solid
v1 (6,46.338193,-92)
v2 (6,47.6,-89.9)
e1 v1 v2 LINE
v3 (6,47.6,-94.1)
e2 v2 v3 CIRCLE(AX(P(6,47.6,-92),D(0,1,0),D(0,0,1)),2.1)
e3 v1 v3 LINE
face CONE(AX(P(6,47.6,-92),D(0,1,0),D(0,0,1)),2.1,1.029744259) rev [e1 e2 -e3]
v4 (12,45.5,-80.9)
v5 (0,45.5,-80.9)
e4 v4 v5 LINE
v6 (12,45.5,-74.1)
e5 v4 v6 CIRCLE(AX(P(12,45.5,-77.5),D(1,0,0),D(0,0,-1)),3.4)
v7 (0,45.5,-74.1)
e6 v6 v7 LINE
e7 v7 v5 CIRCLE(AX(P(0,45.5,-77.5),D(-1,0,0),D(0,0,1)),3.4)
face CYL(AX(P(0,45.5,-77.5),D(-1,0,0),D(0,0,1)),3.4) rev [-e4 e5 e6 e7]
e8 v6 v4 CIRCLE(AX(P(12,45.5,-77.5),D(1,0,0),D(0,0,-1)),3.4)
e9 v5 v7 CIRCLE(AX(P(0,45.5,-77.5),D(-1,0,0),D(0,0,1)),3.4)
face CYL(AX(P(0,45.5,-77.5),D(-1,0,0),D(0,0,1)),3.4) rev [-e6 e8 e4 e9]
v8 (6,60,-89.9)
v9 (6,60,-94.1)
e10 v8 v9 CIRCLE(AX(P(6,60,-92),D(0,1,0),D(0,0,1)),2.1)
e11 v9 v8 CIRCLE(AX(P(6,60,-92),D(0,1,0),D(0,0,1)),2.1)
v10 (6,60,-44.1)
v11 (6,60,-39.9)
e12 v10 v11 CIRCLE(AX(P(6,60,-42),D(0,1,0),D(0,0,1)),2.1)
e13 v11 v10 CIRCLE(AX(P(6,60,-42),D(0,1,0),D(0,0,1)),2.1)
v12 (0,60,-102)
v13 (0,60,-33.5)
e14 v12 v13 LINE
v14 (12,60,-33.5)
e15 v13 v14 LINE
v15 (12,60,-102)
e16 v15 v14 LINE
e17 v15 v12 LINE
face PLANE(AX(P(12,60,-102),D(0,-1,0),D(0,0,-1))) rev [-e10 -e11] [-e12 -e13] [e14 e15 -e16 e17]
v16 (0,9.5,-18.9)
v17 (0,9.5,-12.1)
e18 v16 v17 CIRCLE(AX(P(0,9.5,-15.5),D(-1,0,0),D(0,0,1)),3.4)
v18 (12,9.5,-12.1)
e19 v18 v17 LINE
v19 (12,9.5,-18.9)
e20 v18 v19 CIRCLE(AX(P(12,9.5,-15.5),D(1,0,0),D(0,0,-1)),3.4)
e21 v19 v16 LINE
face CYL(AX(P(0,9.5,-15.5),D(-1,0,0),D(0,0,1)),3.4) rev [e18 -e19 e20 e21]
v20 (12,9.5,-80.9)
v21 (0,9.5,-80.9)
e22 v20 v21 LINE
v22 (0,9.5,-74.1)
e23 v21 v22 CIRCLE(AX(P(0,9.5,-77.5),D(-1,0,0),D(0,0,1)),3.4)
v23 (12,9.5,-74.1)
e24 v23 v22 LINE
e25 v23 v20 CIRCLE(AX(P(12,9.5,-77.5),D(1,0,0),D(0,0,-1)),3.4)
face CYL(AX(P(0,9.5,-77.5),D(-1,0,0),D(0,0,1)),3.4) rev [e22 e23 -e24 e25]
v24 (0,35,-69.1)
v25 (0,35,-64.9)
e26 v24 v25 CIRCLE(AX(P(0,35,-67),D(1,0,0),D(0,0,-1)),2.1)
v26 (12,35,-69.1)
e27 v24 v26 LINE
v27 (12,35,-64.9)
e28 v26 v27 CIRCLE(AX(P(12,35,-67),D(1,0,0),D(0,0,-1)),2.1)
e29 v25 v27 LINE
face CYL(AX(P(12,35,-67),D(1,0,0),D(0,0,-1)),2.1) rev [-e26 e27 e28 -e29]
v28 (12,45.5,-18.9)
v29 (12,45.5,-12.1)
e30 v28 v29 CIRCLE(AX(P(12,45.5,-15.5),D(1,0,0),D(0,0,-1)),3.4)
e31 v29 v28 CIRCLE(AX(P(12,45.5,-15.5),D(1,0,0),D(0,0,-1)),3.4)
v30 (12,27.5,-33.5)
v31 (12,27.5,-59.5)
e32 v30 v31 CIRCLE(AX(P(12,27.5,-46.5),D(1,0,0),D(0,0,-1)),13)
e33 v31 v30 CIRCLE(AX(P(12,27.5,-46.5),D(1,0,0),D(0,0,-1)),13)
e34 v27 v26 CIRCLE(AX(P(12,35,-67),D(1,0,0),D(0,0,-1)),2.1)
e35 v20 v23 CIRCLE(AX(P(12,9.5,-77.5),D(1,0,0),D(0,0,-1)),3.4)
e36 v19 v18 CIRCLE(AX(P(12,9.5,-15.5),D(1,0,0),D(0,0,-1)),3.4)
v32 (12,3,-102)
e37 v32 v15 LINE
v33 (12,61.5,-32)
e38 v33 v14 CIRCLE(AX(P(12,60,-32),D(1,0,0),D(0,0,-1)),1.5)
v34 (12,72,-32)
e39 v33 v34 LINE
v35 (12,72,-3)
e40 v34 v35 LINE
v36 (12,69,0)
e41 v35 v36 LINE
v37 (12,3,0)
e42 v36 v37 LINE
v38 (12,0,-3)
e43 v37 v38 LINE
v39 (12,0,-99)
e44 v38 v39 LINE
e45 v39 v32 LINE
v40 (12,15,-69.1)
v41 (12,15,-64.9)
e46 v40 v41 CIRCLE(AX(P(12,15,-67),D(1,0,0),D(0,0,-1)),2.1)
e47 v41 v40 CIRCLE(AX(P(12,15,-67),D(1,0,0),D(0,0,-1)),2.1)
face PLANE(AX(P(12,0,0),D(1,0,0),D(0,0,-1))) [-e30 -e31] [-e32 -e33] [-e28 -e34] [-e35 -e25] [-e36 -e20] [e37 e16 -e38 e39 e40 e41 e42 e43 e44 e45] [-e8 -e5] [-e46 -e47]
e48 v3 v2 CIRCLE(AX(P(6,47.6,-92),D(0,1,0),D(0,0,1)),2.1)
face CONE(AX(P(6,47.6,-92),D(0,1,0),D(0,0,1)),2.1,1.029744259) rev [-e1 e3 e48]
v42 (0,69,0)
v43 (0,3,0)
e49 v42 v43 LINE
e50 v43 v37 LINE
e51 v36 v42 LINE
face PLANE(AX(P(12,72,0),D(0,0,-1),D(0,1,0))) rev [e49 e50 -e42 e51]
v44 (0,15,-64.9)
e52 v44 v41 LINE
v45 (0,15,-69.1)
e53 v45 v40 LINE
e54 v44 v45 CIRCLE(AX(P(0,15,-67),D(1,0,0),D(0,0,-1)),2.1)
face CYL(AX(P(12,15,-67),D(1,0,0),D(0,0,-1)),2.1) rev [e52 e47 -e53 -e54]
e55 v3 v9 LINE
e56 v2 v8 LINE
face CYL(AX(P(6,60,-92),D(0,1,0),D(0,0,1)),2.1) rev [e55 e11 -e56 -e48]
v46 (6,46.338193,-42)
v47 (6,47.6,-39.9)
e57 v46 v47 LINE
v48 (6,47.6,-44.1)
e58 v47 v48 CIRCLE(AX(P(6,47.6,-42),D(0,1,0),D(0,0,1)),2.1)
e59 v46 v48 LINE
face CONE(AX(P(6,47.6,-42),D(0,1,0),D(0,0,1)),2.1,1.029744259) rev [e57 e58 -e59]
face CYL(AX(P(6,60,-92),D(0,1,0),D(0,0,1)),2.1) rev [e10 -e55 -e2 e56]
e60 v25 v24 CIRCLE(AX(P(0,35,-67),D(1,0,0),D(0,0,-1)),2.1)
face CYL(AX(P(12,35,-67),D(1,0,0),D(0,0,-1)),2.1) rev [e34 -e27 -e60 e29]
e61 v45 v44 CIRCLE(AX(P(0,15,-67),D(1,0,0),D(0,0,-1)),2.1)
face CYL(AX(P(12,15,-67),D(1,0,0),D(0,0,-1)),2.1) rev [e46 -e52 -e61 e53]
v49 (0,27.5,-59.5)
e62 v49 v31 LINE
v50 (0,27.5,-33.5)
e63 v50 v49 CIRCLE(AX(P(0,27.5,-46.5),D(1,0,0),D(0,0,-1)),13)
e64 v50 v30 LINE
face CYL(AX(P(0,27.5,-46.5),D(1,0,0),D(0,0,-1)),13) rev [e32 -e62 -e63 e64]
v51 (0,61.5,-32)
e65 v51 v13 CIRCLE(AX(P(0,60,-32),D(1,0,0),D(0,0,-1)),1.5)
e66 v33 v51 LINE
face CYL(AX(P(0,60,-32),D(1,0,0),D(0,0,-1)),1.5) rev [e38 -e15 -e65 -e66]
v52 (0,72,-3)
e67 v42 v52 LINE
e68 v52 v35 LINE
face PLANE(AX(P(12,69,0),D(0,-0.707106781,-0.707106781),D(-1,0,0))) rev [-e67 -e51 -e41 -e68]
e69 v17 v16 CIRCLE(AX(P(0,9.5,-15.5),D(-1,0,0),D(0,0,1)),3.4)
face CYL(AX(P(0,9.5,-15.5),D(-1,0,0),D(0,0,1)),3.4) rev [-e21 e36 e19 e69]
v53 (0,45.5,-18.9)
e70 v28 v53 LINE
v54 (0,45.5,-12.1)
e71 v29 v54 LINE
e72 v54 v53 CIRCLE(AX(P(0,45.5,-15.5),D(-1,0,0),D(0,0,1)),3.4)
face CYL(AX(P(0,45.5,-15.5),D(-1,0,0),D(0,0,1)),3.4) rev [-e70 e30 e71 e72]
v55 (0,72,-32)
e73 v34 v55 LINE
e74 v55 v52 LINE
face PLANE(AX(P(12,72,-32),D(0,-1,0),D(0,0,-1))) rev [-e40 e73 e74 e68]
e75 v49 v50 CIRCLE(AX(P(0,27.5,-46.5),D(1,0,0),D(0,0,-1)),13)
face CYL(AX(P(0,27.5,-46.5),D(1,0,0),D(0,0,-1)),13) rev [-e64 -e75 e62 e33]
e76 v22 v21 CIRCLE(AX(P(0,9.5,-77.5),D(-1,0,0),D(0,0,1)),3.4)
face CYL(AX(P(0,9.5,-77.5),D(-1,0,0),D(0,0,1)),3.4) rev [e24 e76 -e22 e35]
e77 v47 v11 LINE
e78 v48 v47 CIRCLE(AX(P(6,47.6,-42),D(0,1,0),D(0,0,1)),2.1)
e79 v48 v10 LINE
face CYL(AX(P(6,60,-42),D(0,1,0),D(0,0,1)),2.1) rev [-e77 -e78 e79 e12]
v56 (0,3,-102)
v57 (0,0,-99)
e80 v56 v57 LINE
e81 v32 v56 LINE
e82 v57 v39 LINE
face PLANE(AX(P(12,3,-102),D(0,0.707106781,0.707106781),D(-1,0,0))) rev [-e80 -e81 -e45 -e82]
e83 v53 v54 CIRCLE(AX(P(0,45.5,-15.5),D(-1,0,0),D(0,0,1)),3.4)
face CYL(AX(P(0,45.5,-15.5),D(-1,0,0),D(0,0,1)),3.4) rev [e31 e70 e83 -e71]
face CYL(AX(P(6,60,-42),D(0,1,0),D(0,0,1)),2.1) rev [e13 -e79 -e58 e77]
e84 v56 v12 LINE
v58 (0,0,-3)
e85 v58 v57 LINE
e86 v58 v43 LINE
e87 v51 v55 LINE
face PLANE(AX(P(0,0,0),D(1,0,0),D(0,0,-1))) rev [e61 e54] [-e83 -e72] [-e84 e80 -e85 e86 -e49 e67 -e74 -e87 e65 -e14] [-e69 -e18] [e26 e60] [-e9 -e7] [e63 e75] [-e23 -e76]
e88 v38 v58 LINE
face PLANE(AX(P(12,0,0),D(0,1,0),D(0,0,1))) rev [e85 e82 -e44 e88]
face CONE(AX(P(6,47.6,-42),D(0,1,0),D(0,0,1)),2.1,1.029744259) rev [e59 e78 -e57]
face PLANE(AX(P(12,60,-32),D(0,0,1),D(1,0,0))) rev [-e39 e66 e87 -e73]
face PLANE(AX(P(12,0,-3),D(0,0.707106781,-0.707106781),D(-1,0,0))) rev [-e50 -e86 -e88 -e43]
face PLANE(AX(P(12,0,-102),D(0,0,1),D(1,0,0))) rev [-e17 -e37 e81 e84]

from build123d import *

# Parameters (mm, degrees)
BOSS_EXTRUDE1_DEPTH   = 12
SKETCH2_R             = 13
CUT_EXTRUDE1_DEPTH    = 126.427269762
M8_TAPPED_HOLE1_D     = 6.8
M8_TAPPED_HOLE1_DEPTH = 19.75
M8_TAPPED_HOLE1_TIP   = 2.042926105
M5_TAPPED_HOLE1_D     = 4.2
M5_TAPPED_HOLE1_DEPTH = 12.4
M5_TAPPED_HOLE1_TIP   = 1.2618073
M5_TAPPED_HOLE2_D     = 4.2
M5_TAPPED_HOLE2_DEPTH = 12.4
M5_TAPPED_HOLE2_TIP   = 1.2618073
CHAMFER1_SIZE         = 3
SKETCH11_R            = 1.5
CUT_EXTRUDE2_DEPTH    = 126.427269762


with BuildPart() as part:
    # Sketch1 → Boss-Extrude1 (new body)
    with BuildSketch(Plane(origin=(0, 0, 0), x_dir=(0, 0, -1), z_dir=(1, 0, 0))):
        Polygon((0, 0), (102, 0), (102, 60), (32, 60), (32, 72), (0, 72), align=None)
    extrude(amount=BOSS_EXTRUDE1_DEPTH)

    # Sketch2 → Cut-Extrude1 (cut, through all)
    with BuildSketch(Plane(origin=(12, 0, 0), x_dir=(0, 0, -1), z_dir=(1, 0, 0))):
        with Locations((46.5, 27.5)):
            Circle(SKETCH2_R)
    extrude(amount=-CUT_EXTRUDE1_DEPTH, mode=Mode.SUBTRACT)

    # M8 Tapped Hole1
    with Locations(Plane.ZY):
        with Locations((-77.5, 45.5), (-77.5, 9.5), (-15.5, 9.5), (-15.5, 45.5)):
            Hole(M8_TAPPED_HOLE1_D / 2, depth=M8_TAPPED_HOLE1_DEPTH)
            with Locations((0, 0, -(M8_TAPPED_HOLE1_DEPTH + M8_TAPPED_HOLE1_TIP / 2))):  # 118° drill point
                Cone(0, M8_TAPPED_HOLE1_D / 2, M8_TAPPED_HOLE1_TIP, mode=Mode.SUBTRACT)

    # M5 Tapped Hole1
    with Locations(Plane(origin=(12, 0, 0), x_dir=(0, 0, -1), z_dir=(1, 0, 0))):
        with Locations((67, 35), (67, 15)):
            Hole(M5_TAPPED_HOLE1_D / 2, depth=M5_TAPPED_HOLE1_DEPTH)
            with Locations((0, 0, -(M5_TAPPED_HOLE1_DEPTH + M5_TAPPED_HOLE1_TIP / 2))):  # 118° drill point
                Cone(0, M5_TAPPED_HOLE1_D / 2, M5_TAPPED_HOLE1_TIP, mode=Mode.SUBTRACT)

    # M5 Tapped Hole2
    with Locations(Plane(origin=(0, 60, 0), x_dir=(1, 0, 0), z_dir=(0, 1, 0))):
        with Locations((6, 42), (6, 92)):
            Hole(M5_TAPPED_HOLE2_D / 2, depth=M5_TAPPED_HOLE2_DEPTH)
            with Locations((0, 0, -(M5_TAPPED_HOLE2_DEPTH + M5_TAPPED_HOLE2_TIP / 2))):  # 118° drill point
                Cone(0, M5_TAPPED_HOLE2_D / 2, M5_TAPPED_HOLE2_TIP, mode=Mode.SUBTRACT)

    # Chamfer1
    chamfer1_edges = [part.edges().sort_by_distance(p)[0] for p in [
        (6, 72, 0),
        (6, 0, -102),
        (6, 0, 0),
    ]]
    chamfer(chamfer1_edges, length=CHAMFER1_SIZE)

    # Sketch11 → Cut-Extrude2 (cut, through all)
    with BuildSketch(Plane(origin=(12, 0, 0), x_dir=(0, 0, -1), z_dir=(1, 0, 0))):
        with Locations((32, 60)):
            Circle(SKETCH11_R)
    extrude(amount=-CUT_EXTRUDE2_DEPTH, mode=Mode.SUBTRACT)


solid = part.part
